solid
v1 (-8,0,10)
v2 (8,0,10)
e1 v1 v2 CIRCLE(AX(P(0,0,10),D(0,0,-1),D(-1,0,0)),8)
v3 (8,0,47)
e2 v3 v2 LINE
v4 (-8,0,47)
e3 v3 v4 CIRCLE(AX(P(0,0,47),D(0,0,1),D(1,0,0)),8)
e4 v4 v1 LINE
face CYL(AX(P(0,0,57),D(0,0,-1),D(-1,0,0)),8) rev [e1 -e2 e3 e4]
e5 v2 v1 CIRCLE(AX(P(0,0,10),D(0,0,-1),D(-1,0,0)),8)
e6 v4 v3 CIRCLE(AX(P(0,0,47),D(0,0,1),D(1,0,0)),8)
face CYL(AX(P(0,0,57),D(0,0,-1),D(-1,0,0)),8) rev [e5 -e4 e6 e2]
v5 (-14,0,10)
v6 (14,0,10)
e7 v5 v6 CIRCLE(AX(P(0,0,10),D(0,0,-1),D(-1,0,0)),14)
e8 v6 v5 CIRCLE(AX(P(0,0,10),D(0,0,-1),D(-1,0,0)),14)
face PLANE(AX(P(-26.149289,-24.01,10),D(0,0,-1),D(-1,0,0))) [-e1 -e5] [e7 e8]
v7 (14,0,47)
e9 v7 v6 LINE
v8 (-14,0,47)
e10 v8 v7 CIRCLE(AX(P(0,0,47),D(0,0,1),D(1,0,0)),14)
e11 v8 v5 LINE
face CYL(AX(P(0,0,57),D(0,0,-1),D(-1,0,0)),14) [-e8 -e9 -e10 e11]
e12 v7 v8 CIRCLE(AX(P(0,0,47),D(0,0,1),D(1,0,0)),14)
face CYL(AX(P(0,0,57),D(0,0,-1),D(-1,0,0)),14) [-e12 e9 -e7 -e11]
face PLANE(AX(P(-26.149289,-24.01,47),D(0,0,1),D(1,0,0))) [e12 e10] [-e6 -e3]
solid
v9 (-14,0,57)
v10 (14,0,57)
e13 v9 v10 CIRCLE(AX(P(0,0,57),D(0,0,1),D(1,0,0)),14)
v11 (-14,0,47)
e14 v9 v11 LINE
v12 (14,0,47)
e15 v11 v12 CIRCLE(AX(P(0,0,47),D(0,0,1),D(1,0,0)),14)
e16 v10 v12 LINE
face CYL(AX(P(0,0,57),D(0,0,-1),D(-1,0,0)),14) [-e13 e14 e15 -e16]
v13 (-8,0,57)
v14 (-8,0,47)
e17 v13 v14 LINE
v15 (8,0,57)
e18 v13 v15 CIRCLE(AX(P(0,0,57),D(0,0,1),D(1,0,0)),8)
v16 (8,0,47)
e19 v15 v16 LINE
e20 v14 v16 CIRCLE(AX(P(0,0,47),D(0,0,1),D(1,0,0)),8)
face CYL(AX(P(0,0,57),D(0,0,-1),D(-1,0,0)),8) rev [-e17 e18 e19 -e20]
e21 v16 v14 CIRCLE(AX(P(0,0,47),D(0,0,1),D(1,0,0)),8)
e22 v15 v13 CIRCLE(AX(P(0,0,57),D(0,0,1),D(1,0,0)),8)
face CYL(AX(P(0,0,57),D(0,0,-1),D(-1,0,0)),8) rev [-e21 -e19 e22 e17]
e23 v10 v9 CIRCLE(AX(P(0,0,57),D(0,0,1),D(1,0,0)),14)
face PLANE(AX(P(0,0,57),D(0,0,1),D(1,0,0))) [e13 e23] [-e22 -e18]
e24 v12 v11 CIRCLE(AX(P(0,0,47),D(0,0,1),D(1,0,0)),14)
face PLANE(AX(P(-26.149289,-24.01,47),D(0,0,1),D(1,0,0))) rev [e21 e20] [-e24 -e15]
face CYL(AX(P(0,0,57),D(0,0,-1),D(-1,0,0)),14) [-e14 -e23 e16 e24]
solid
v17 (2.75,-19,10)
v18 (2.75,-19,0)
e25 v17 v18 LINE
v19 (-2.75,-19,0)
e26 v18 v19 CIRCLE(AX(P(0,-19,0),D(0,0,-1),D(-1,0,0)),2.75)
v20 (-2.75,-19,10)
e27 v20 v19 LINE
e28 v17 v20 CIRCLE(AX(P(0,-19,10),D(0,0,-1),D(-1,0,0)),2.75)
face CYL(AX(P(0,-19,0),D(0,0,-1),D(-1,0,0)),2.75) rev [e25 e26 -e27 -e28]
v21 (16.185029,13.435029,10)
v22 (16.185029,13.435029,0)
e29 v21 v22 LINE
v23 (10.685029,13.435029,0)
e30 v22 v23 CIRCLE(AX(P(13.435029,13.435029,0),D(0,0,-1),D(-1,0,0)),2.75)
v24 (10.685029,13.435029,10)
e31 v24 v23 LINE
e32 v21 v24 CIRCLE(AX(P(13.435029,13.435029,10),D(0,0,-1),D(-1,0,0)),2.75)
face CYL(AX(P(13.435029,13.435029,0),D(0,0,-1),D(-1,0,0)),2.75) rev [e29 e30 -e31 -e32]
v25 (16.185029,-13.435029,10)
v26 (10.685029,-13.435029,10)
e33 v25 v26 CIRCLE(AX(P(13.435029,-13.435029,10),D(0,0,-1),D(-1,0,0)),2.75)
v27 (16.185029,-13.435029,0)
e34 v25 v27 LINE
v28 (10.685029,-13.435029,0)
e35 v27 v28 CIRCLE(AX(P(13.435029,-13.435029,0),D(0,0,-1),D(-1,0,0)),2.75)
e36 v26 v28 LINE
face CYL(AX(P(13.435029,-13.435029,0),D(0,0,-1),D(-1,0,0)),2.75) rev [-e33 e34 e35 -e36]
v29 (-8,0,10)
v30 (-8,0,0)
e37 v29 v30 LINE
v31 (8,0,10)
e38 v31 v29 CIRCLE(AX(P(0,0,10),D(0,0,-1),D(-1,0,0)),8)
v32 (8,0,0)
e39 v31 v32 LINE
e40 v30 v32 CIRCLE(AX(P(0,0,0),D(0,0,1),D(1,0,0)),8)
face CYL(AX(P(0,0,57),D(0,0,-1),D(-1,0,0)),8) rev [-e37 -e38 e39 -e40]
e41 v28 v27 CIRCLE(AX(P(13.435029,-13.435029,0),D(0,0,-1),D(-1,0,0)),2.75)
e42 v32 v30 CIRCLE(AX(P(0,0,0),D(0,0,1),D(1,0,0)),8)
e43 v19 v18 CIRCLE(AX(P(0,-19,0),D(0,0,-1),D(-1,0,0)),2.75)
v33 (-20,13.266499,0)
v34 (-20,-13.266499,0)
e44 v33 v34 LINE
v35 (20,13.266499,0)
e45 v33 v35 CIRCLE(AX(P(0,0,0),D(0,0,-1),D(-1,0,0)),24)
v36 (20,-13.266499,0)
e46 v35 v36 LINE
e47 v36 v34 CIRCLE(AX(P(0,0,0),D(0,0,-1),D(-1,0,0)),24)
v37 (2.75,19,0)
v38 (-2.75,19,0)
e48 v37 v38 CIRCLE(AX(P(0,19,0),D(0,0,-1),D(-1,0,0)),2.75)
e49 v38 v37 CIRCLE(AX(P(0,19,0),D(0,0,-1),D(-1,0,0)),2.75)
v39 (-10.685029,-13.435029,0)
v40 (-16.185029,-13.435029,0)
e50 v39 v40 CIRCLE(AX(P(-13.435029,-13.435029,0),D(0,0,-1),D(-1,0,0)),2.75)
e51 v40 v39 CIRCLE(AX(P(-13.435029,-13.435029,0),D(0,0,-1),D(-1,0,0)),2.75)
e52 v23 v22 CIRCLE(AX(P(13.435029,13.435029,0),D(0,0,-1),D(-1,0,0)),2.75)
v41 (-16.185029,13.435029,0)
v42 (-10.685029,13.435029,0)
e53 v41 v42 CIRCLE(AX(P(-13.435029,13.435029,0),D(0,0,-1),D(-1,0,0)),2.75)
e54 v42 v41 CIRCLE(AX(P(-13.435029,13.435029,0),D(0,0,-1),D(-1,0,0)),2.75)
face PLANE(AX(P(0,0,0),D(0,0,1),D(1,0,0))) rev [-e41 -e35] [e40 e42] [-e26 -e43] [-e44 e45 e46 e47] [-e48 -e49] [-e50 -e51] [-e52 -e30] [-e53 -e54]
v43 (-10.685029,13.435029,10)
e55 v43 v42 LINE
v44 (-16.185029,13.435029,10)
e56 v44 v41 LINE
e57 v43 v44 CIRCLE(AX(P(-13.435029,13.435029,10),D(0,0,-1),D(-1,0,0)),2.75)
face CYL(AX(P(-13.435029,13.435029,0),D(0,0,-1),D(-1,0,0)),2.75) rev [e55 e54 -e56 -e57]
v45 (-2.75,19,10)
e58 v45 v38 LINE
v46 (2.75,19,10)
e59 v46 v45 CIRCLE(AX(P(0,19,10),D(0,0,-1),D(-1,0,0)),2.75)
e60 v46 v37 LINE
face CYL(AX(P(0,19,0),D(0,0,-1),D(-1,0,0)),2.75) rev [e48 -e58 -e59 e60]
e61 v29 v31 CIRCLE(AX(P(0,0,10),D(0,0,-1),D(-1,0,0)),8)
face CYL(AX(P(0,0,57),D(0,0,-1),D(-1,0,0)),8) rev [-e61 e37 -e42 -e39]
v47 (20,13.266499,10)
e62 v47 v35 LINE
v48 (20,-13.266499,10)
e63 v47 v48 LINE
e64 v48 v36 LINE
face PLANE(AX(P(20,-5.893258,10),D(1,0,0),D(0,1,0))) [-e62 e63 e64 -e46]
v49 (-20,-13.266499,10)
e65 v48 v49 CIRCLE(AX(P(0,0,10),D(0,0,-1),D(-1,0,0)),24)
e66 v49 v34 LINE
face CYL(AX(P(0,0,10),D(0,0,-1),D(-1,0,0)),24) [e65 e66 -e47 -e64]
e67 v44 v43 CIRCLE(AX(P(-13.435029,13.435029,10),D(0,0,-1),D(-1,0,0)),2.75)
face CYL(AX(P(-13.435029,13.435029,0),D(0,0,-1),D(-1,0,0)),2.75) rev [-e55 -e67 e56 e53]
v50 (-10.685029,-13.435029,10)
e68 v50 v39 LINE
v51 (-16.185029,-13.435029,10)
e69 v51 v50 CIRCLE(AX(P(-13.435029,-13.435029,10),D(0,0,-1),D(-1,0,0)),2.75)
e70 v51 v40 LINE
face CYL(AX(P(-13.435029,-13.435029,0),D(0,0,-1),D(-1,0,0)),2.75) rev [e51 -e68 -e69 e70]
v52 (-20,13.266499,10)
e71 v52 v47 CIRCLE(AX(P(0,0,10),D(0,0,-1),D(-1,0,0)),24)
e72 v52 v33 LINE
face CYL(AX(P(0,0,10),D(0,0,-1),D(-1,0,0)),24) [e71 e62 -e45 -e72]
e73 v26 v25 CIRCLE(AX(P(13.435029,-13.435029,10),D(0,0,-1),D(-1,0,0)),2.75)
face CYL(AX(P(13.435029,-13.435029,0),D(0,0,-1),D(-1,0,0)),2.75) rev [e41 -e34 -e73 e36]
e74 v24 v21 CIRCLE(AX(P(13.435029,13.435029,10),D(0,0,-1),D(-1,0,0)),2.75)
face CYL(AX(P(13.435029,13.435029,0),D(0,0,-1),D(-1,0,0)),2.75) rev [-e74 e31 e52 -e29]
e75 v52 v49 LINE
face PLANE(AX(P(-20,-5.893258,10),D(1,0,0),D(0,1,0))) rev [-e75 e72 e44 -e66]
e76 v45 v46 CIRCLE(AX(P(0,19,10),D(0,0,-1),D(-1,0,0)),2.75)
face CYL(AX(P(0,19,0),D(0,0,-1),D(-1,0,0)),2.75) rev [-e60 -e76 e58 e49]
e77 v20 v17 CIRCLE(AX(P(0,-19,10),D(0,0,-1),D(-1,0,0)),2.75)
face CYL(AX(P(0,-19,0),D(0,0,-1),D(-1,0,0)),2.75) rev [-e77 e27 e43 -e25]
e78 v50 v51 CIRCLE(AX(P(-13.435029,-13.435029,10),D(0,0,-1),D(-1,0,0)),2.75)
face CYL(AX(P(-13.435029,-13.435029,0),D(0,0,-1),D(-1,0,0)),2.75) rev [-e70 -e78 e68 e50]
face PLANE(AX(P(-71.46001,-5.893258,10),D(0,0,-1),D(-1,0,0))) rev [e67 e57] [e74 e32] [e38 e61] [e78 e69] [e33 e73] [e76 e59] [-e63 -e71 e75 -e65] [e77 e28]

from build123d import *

# Parameters (mm, degrees)
SKETCH1_R                  = 14
SKETCH1_R_2                = 8
BOSS_EXTRUDE1_DEPTH        = 57
SKETCH2_R                  = 14
SKETCH2_R_2                = 8
BOSS_EXTRUDE2_DEPTH        = 10
F_5_5_5_5_DIAMETER_HOLE1_D = 5.5
SPLIT1_SURFACE_1_BACK      = 85.575
SPLIT1_SURFACE_1_DEPTH     = 171.15
SPLIT1_SURFACE_2_BACK      = 85.575
SPLIT1_SURFACE_2_DEPTH     = 171.15


with BuildPart() as part:
    # Sketch1 → Boss-Extrude1 (new body)
    with BuildSketch(Plane.XY):
        with Locations(Location((0, 0, 0), (0, 0, 180))):
            Circle(SKETCH1_R)
        with Locations(Location((0, 0, 0), (0, 0, 180))):
            Circle(SKETCH1_R_2, mode=Mode.SUBTRACT)
    extrude(amount=BOSS_EXTRUDE1_DEPTH)

    # Sketch2 → Boss-Extrude2 (add)
    # profile 1 of 2: a face of its own
    with BuildSketch(Plane(origin=(0, 0, 0), x_dir=(-1, 0, 0), z_dir=(0, 0, -1))):
        with BuildLine():
            ThreePointArc((20, 13.266499161), (0, 24), (-20, 13.266499161))
            Line((-20, 13.266499161), (-20, -13.266499161))
            ThreePointArc((-20, -13.266499161), (0, -24), (20, -13.266499161))
            Line((20, -13.266499161), (20, 13.266499161))
        make_face()
        Circle(SKETCH2_R, mode=Mode.SUBTRACT)
    # profile 2 of 2: a face of its own
    with BuildSketch(Plane(origin=(0, 0, 0), x_dir=(-1, 0, 0), z_dir=(0, 0, -1))):
        Circle(SKETCH2_R)
        Circle(SKETCH2_R_2, mode=Mode.SUBTRACT)
    extrude(amount=-BOSS_EXTRUDE2_DEPTH)

    # Ø5.5 (5.5) Diameter Hole1 (through all)
    with Locations(Plane(origin=(0, 0, 0), x_dir=(-1, 0, 0), z_dir=(0, 0, -1))):
        with Locations((0, 19), (-13.435028843, 13.435028843), (13.435028843, 13.435028843)):
            f_5_5_5_5_diameter_hole1 = Hole(F_5_5_5_5_DIAMETER_HOLE1_D / 2)

    # Mirror1: Ø5.5 (5.5) Diameter Hole1 across plane
    add(f_5_5_5_5_diameter_hole1.mirror(Plane.ZX), mode=Mode.SUBTRACT)


with BuildPart() as body_2:
    # Split1: the piece behind the surface
    add(part.part)
    # Split1 surface: a surface, the sketch's curves swept straight by 171.15 mm
    with BuildLine(Plane(origin=(0, 0, 0), x_dir=(1, 0, 0), z_dir=(0, 1, 0)).offset(-SPLIT1_SURFACE_1_BACK), mode=Mode.PRIVATE) as split1_surface_1_path:
        Line((-26.149288563, -10), (31.044229279, -10))
        Line((31.044229279, -10), (31.044229279, -47))
        Line((31.044229279, -47), (-26.149288563, -47))
        Line((-26.149288563, -47), (-26.149288563, -10))
    split1_surface_1 = Shell.extrude(split1_surface_1_path.wire(), (0 * SPLIT1_SURFACE_1_DEPTH, 1 * SPLIT1_SURFACE_1_DEPTH, 0 * SPLIT1_SURFACE_1_DEPTH))
    split(bisect_by=split1_surface_1, keep=Keep.BOTTOM)


with BuildPart() as part_1:
    add(part.part)

    # Split1: split by a surface, the side it looks to stays
    # Split1 surface: a surface, the sketch's curves swept straight by 171.15 mm
    with BuildLine(Plane(origin=(0, 0, 0), x_dir=(1, 0, 0), z_dir=(0, 1, 0)).offset(-SPLIT1_SURFACE_2_BACK), mode=Mode.PRIVATE) as split1_surface_2_path:
        Line((-26.149288563, -10), (31.044229279, -10))
        Line((31.044229279, -10), (31.044229279, -47))
        Line((31.044229279, -47), (-26.149288563, -47))
        Line((-26.149288563, -47), (-26.149288563, -10))
    split1_surface_2 = Shell.extrude(split1_surface_2_path.wire(), (0 * SPLIT1_SURFACE_2_DEPTH, 1 * SPLIT1_SURFACE_2_DEPTH, 0 * SPLIT1_SURFACE_2_DEPTH))
    split(bisect_by=split1_surface_2, keep=Keep.TOP)


solid = Compound([body_2.part, part_1.part])
